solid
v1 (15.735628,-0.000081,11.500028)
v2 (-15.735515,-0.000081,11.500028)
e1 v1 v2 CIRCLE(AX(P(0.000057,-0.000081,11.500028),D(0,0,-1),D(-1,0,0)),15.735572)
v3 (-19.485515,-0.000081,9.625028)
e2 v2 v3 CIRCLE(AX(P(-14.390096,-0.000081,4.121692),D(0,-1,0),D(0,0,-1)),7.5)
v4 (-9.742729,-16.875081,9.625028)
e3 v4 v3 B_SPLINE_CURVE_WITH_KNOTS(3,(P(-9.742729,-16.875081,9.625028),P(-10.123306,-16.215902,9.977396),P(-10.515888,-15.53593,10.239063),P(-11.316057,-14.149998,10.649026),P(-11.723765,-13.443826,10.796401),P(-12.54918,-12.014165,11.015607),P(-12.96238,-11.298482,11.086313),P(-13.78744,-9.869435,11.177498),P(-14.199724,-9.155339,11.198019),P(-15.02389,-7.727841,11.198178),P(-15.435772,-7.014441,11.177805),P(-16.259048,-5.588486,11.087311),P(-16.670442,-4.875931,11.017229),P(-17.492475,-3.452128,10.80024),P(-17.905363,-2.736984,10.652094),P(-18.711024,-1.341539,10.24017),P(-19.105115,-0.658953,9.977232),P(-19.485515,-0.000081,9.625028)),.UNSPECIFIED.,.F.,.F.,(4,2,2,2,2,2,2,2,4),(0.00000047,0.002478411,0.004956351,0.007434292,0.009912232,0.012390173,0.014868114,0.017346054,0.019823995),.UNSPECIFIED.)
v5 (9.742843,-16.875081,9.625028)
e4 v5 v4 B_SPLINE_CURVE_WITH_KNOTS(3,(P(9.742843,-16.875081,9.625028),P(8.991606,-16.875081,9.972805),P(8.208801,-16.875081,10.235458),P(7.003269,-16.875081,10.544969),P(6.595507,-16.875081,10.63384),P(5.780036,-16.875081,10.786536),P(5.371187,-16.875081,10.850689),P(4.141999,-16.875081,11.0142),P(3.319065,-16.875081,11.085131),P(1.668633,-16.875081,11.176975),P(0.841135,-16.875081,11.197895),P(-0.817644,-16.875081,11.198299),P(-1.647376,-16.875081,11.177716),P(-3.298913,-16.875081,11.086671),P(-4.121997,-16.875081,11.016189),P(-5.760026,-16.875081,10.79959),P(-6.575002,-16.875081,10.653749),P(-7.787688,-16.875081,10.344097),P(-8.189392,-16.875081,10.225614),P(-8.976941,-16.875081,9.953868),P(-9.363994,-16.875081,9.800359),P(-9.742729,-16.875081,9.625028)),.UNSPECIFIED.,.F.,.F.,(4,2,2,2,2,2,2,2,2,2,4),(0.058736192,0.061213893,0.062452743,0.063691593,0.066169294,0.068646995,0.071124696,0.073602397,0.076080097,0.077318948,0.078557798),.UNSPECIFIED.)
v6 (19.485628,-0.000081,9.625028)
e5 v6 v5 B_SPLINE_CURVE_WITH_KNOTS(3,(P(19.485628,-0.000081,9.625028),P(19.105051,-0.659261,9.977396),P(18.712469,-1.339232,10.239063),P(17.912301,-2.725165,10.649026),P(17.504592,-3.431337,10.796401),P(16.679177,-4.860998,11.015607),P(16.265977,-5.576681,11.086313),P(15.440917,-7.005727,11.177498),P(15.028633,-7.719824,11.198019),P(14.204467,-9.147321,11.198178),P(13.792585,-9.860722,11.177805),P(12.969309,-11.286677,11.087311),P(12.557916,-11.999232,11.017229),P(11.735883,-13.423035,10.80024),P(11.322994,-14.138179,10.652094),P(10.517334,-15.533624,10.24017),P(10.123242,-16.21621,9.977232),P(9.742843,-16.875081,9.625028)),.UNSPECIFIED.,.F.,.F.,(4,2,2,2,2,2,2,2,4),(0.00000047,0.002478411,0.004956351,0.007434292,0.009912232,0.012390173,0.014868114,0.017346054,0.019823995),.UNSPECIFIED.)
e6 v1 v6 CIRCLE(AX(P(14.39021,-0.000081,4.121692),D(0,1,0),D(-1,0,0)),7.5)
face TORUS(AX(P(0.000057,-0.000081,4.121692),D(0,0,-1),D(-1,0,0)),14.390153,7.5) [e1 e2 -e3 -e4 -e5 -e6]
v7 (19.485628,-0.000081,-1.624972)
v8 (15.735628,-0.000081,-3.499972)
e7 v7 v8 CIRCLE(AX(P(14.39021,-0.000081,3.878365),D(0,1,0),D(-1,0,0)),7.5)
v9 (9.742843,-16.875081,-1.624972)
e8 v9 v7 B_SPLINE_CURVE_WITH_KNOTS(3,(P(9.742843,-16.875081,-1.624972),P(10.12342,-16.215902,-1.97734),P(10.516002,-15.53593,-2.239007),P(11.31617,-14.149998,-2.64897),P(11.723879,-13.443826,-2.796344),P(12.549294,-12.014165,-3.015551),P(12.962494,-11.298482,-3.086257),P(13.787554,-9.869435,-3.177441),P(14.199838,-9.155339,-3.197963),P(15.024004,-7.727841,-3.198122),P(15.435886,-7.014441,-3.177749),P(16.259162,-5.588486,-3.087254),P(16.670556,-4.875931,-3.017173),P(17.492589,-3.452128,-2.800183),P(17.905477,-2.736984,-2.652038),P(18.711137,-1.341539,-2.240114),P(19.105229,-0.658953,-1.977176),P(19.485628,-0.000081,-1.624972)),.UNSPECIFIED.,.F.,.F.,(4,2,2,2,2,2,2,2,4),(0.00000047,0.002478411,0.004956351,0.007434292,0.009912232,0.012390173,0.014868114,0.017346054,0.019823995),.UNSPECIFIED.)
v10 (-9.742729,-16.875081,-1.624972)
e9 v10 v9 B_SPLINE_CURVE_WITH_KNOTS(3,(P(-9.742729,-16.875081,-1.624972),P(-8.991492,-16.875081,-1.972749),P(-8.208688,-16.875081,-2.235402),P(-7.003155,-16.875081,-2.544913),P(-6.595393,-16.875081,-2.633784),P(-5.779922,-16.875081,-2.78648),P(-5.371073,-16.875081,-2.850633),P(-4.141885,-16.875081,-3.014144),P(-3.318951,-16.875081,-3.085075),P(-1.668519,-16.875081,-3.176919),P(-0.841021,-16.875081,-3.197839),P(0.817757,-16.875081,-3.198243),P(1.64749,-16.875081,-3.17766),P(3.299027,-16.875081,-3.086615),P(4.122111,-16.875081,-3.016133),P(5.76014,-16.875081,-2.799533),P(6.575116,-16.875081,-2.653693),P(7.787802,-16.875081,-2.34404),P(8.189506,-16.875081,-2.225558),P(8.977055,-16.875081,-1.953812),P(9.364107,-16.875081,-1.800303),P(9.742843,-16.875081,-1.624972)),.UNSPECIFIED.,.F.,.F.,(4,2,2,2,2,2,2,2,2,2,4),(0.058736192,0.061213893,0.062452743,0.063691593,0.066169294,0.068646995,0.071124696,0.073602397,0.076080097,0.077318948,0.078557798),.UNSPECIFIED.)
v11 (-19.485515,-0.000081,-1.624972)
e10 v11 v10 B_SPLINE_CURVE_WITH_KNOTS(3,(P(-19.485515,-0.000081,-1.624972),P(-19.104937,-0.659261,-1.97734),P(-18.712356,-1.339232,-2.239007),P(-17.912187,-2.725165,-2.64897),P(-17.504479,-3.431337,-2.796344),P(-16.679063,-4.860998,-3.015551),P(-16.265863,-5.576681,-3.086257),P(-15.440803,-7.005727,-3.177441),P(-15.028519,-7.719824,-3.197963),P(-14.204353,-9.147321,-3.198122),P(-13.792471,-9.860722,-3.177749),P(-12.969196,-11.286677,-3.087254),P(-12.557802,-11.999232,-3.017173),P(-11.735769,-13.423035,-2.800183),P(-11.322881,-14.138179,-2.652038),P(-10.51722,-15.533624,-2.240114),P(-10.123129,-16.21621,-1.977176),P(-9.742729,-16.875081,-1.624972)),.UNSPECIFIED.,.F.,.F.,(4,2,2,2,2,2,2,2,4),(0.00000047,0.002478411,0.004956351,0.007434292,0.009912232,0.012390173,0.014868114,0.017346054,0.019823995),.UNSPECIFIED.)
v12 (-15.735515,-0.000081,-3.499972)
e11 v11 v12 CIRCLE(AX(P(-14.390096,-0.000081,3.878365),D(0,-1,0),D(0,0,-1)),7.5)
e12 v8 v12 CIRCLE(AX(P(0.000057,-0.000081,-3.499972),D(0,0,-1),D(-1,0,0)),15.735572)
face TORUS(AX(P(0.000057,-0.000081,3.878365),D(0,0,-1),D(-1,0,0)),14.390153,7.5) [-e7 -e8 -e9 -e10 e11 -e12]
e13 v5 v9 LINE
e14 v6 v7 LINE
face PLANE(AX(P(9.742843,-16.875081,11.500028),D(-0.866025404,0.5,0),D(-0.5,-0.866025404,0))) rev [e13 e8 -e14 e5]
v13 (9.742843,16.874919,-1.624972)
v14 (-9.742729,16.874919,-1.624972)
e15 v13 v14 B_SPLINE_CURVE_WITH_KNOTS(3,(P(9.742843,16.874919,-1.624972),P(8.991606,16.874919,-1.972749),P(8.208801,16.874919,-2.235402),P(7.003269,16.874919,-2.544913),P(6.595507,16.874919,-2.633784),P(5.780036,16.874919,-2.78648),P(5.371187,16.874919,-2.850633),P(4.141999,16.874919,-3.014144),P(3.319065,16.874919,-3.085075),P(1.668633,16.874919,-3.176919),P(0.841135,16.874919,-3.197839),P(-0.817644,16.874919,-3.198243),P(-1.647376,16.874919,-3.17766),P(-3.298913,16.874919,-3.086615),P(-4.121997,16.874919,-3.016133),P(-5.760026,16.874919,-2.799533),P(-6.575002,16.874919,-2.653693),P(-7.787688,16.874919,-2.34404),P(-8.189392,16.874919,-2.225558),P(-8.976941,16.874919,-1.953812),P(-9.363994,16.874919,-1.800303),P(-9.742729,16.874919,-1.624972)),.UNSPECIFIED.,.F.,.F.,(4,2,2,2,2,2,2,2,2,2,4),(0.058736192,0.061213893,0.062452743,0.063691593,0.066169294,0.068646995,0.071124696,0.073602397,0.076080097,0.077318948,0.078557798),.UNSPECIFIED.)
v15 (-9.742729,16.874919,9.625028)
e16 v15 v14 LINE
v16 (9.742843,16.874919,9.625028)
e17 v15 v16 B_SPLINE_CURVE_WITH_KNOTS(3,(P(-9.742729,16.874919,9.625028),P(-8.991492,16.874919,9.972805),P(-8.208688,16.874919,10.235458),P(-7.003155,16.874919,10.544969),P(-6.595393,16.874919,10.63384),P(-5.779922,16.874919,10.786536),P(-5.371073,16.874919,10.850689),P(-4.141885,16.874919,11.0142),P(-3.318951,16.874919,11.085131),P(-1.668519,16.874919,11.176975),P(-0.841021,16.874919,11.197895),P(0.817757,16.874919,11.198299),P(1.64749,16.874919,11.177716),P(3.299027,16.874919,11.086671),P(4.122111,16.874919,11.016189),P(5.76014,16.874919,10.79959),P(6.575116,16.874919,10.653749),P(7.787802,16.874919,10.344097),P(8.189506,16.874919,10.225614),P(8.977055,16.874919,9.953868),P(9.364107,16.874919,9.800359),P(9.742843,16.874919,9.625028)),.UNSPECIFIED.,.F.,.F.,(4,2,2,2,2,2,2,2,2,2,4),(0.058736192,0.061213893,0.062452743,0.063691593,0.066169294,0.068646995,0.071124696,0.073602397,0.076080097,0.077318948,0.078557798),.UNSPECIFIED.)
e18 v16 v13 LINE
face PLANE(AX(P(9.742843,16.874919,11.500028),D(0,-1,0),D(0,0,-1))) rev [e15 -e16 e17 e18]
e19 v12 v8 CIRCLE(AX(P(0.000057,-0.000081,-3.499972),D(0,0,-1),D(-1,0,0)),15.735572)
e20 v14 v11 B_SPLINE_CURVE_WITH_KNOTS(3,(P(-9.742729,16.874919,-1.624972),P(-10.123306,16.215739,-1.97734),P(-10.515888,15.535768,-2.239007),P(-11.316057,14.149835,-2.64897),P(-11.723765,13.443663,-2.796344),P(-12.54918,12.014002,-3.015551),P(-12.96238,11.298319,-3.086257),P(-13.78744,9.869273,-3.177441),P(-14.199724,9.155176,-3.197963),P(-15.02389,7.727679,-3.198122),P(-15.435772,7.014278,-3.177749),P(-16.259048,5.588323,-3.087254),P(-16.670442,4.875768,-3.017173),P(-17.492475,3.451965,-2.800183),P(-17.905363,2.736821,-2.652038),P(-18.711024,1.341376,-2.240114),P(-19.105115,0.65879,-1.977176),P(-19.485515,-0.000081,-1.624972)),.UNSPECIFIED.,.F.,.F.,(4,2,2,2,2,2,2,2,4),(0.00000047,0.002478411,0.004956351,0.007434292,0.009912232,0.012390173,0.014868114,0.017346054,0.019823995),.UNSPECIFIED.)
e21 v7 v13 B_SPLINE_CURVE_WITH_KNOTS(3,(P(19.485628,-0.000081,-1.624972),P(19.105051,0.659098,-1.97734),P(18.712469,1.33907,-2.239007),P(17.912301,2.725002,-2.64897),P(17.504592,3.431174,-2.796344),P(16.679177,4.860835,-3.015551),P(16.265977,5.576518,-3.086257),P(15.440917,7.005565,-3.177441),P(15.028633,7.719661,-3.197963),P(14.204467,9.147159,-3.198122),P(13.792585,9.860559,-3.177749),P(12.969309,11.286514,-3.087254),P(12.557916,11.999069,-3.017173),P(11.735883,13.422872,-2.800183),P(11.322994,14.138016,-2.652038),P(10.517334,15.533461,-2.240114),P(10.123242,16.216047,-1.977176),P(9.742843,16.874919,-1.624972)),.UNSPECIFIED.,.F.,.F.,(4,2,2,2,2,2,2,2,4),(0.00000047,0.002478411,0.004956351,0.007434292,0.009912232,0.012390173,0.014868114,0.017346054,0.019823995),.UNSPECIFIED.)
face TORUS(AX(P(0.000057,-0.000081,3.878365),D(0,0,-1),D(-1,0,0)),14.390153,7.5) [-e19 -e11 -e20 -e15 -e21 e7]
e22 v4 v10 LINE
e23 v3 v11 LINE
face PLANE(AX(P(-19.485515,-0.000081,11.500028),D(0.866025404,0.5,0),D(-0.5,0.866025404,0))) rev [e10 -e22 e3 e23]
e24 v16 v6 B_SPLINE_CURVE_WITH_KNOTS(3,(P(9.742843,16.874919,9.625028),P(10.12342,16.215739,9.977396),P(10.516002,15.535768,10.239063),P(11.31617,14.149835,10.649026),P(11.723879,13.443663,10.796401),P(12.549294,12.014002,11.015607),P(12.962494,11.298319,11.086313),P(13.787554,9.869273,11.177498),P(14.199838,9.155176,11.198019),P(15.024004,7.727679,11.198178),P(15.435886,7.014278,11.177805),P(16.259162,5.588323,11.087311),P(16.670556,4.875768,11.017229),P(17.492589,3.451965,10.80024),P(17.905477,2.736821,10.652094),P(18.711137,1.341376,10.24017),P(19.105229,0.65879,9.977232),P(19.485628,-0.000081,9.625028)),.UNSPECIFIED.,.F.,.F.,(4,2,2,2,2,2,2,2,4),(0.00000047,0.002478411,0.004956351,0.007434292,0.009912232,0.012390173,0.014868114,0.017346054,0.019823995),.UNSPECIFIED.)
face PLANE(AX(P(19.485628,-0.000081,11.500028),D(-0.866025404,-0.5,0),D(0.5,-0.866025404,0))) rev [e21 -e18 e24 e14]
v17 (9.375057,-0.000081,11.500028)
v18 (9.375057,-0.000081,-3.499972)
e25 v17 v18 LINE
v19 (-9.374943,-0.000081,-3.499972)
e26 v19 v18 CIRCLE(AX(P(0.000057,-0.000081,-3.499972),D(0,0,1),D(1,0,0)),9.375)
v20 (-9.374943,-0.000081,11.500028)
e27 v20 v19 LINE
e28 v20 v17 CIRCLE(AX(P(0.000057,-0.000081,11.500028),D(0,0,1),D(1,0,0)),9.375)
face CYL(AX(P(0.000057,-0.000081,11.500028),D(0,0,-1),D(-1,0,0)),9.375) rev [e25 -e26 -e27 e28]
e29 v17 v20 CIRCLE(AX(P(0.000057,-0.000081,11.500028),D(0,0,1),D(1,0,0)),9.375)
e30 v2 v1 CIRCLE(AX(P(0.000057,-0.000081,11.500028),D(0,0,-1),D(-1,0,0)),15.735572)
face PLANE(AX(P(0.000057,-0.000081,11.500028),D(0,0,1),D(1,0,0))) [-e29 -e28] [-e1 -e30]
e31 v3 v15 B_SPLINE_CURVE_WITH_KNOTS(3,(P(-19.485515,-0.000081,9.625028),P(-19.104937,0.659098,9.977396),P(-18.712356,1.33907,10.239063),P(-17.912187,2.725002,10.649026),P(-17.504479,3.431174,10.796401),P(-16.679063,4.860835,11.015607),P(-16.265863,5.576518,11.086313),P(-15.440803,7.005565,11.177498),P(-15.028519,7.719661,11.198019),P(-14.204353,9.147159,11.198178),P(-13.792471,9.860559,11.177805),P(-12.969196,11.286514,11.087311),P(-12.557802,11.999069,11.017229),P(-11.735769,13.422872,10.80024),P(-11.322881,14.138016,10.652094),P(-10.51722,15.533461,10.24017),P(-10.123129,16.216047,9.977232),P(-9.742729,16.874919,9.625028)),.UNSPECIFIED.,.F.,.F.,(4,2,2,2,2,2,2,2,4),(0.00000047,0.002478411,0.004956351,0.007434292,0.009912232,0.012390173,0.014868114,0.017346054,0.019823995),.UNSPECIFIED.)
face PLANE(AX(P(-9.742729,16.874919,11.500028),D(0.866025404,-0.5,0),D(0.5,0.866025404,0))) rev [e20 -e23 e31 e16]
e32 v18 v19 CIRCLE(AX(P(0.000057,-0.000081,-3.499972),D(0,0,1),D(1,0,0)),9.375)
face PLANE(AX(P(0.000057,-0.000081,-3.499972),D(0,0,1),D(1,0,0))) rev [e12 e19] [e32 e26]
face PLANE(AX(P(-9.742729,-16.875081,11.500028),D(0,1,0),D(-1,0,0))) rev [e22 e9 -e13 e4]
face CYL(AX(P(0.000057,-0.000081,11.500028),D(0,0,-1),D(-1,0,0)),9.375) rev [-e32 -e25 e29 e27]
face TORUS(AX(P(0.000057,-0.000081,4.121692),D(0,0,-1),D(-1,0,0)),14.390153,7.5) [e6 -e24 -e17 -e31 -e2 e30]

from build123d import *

# Parameters (mm, degrees)
SKETCH5_R           = 5
BOSS_EXTRUDE2_DEPTH = 8
SCALE_1_SCALE       = 1.875


with BuildPart() as part:
    # Sketch5 → Boss-Extrude2 (new body)
    with BuildSketch(Plane.XY):
        Polygon((10.392304845, 0), (5.196152423, 9), (-5.196152423, 9), (-10.392304845, 0), (-5.196152423, -9), (5.196152423, -9), align=None)
        Circle(SKETCH5_R, mode=Mode.SUBTRACT)
    extrude(amount=BOSS_EXTRUDE2_DEPTH)

    # Sketch6 → Cut-Revolve2 (revolve, cut)
    with BuildSketch(Plane(origin=(0, 0, 0), x_dir=(1, 0, 0), z_dir=(0, 1, 0))):
        with BuildLine():
            Line((-10.392304845, 0), (-10.392304845, -1))
            ThreePointArc((-10.392304845, -1), (-9.463602824, -0.357404043), (-8.392304845, 0))
            Line((-8.392304845, 0), (-10.392304845, 0))
        make_face()
        with BuildLine():
            Line((-10.392304845, -8), (-8.392304845, -8))
            ThreePointArc((-8.392304845, -8), (-9.463602824, -7.642595957), (-10.392304845, -7))
            Line((-10.392304845, -7), (-10.392304845, -8))
        make_face()
    revolve(axis=Axis((0, 0, 0), (0, 0, 1)), mode=Mode.SUBTRACT)


with BuildPart() as part_1:
    # Scale 1: scaled about (-5.25e-07, 1.59e-07, 3.999997472)
    add(part.part.scale(SCALE_1_SCALE).moved(Location((4.59e-07, -1.39e-07, -3.499997788))))


solid = part_1.part
